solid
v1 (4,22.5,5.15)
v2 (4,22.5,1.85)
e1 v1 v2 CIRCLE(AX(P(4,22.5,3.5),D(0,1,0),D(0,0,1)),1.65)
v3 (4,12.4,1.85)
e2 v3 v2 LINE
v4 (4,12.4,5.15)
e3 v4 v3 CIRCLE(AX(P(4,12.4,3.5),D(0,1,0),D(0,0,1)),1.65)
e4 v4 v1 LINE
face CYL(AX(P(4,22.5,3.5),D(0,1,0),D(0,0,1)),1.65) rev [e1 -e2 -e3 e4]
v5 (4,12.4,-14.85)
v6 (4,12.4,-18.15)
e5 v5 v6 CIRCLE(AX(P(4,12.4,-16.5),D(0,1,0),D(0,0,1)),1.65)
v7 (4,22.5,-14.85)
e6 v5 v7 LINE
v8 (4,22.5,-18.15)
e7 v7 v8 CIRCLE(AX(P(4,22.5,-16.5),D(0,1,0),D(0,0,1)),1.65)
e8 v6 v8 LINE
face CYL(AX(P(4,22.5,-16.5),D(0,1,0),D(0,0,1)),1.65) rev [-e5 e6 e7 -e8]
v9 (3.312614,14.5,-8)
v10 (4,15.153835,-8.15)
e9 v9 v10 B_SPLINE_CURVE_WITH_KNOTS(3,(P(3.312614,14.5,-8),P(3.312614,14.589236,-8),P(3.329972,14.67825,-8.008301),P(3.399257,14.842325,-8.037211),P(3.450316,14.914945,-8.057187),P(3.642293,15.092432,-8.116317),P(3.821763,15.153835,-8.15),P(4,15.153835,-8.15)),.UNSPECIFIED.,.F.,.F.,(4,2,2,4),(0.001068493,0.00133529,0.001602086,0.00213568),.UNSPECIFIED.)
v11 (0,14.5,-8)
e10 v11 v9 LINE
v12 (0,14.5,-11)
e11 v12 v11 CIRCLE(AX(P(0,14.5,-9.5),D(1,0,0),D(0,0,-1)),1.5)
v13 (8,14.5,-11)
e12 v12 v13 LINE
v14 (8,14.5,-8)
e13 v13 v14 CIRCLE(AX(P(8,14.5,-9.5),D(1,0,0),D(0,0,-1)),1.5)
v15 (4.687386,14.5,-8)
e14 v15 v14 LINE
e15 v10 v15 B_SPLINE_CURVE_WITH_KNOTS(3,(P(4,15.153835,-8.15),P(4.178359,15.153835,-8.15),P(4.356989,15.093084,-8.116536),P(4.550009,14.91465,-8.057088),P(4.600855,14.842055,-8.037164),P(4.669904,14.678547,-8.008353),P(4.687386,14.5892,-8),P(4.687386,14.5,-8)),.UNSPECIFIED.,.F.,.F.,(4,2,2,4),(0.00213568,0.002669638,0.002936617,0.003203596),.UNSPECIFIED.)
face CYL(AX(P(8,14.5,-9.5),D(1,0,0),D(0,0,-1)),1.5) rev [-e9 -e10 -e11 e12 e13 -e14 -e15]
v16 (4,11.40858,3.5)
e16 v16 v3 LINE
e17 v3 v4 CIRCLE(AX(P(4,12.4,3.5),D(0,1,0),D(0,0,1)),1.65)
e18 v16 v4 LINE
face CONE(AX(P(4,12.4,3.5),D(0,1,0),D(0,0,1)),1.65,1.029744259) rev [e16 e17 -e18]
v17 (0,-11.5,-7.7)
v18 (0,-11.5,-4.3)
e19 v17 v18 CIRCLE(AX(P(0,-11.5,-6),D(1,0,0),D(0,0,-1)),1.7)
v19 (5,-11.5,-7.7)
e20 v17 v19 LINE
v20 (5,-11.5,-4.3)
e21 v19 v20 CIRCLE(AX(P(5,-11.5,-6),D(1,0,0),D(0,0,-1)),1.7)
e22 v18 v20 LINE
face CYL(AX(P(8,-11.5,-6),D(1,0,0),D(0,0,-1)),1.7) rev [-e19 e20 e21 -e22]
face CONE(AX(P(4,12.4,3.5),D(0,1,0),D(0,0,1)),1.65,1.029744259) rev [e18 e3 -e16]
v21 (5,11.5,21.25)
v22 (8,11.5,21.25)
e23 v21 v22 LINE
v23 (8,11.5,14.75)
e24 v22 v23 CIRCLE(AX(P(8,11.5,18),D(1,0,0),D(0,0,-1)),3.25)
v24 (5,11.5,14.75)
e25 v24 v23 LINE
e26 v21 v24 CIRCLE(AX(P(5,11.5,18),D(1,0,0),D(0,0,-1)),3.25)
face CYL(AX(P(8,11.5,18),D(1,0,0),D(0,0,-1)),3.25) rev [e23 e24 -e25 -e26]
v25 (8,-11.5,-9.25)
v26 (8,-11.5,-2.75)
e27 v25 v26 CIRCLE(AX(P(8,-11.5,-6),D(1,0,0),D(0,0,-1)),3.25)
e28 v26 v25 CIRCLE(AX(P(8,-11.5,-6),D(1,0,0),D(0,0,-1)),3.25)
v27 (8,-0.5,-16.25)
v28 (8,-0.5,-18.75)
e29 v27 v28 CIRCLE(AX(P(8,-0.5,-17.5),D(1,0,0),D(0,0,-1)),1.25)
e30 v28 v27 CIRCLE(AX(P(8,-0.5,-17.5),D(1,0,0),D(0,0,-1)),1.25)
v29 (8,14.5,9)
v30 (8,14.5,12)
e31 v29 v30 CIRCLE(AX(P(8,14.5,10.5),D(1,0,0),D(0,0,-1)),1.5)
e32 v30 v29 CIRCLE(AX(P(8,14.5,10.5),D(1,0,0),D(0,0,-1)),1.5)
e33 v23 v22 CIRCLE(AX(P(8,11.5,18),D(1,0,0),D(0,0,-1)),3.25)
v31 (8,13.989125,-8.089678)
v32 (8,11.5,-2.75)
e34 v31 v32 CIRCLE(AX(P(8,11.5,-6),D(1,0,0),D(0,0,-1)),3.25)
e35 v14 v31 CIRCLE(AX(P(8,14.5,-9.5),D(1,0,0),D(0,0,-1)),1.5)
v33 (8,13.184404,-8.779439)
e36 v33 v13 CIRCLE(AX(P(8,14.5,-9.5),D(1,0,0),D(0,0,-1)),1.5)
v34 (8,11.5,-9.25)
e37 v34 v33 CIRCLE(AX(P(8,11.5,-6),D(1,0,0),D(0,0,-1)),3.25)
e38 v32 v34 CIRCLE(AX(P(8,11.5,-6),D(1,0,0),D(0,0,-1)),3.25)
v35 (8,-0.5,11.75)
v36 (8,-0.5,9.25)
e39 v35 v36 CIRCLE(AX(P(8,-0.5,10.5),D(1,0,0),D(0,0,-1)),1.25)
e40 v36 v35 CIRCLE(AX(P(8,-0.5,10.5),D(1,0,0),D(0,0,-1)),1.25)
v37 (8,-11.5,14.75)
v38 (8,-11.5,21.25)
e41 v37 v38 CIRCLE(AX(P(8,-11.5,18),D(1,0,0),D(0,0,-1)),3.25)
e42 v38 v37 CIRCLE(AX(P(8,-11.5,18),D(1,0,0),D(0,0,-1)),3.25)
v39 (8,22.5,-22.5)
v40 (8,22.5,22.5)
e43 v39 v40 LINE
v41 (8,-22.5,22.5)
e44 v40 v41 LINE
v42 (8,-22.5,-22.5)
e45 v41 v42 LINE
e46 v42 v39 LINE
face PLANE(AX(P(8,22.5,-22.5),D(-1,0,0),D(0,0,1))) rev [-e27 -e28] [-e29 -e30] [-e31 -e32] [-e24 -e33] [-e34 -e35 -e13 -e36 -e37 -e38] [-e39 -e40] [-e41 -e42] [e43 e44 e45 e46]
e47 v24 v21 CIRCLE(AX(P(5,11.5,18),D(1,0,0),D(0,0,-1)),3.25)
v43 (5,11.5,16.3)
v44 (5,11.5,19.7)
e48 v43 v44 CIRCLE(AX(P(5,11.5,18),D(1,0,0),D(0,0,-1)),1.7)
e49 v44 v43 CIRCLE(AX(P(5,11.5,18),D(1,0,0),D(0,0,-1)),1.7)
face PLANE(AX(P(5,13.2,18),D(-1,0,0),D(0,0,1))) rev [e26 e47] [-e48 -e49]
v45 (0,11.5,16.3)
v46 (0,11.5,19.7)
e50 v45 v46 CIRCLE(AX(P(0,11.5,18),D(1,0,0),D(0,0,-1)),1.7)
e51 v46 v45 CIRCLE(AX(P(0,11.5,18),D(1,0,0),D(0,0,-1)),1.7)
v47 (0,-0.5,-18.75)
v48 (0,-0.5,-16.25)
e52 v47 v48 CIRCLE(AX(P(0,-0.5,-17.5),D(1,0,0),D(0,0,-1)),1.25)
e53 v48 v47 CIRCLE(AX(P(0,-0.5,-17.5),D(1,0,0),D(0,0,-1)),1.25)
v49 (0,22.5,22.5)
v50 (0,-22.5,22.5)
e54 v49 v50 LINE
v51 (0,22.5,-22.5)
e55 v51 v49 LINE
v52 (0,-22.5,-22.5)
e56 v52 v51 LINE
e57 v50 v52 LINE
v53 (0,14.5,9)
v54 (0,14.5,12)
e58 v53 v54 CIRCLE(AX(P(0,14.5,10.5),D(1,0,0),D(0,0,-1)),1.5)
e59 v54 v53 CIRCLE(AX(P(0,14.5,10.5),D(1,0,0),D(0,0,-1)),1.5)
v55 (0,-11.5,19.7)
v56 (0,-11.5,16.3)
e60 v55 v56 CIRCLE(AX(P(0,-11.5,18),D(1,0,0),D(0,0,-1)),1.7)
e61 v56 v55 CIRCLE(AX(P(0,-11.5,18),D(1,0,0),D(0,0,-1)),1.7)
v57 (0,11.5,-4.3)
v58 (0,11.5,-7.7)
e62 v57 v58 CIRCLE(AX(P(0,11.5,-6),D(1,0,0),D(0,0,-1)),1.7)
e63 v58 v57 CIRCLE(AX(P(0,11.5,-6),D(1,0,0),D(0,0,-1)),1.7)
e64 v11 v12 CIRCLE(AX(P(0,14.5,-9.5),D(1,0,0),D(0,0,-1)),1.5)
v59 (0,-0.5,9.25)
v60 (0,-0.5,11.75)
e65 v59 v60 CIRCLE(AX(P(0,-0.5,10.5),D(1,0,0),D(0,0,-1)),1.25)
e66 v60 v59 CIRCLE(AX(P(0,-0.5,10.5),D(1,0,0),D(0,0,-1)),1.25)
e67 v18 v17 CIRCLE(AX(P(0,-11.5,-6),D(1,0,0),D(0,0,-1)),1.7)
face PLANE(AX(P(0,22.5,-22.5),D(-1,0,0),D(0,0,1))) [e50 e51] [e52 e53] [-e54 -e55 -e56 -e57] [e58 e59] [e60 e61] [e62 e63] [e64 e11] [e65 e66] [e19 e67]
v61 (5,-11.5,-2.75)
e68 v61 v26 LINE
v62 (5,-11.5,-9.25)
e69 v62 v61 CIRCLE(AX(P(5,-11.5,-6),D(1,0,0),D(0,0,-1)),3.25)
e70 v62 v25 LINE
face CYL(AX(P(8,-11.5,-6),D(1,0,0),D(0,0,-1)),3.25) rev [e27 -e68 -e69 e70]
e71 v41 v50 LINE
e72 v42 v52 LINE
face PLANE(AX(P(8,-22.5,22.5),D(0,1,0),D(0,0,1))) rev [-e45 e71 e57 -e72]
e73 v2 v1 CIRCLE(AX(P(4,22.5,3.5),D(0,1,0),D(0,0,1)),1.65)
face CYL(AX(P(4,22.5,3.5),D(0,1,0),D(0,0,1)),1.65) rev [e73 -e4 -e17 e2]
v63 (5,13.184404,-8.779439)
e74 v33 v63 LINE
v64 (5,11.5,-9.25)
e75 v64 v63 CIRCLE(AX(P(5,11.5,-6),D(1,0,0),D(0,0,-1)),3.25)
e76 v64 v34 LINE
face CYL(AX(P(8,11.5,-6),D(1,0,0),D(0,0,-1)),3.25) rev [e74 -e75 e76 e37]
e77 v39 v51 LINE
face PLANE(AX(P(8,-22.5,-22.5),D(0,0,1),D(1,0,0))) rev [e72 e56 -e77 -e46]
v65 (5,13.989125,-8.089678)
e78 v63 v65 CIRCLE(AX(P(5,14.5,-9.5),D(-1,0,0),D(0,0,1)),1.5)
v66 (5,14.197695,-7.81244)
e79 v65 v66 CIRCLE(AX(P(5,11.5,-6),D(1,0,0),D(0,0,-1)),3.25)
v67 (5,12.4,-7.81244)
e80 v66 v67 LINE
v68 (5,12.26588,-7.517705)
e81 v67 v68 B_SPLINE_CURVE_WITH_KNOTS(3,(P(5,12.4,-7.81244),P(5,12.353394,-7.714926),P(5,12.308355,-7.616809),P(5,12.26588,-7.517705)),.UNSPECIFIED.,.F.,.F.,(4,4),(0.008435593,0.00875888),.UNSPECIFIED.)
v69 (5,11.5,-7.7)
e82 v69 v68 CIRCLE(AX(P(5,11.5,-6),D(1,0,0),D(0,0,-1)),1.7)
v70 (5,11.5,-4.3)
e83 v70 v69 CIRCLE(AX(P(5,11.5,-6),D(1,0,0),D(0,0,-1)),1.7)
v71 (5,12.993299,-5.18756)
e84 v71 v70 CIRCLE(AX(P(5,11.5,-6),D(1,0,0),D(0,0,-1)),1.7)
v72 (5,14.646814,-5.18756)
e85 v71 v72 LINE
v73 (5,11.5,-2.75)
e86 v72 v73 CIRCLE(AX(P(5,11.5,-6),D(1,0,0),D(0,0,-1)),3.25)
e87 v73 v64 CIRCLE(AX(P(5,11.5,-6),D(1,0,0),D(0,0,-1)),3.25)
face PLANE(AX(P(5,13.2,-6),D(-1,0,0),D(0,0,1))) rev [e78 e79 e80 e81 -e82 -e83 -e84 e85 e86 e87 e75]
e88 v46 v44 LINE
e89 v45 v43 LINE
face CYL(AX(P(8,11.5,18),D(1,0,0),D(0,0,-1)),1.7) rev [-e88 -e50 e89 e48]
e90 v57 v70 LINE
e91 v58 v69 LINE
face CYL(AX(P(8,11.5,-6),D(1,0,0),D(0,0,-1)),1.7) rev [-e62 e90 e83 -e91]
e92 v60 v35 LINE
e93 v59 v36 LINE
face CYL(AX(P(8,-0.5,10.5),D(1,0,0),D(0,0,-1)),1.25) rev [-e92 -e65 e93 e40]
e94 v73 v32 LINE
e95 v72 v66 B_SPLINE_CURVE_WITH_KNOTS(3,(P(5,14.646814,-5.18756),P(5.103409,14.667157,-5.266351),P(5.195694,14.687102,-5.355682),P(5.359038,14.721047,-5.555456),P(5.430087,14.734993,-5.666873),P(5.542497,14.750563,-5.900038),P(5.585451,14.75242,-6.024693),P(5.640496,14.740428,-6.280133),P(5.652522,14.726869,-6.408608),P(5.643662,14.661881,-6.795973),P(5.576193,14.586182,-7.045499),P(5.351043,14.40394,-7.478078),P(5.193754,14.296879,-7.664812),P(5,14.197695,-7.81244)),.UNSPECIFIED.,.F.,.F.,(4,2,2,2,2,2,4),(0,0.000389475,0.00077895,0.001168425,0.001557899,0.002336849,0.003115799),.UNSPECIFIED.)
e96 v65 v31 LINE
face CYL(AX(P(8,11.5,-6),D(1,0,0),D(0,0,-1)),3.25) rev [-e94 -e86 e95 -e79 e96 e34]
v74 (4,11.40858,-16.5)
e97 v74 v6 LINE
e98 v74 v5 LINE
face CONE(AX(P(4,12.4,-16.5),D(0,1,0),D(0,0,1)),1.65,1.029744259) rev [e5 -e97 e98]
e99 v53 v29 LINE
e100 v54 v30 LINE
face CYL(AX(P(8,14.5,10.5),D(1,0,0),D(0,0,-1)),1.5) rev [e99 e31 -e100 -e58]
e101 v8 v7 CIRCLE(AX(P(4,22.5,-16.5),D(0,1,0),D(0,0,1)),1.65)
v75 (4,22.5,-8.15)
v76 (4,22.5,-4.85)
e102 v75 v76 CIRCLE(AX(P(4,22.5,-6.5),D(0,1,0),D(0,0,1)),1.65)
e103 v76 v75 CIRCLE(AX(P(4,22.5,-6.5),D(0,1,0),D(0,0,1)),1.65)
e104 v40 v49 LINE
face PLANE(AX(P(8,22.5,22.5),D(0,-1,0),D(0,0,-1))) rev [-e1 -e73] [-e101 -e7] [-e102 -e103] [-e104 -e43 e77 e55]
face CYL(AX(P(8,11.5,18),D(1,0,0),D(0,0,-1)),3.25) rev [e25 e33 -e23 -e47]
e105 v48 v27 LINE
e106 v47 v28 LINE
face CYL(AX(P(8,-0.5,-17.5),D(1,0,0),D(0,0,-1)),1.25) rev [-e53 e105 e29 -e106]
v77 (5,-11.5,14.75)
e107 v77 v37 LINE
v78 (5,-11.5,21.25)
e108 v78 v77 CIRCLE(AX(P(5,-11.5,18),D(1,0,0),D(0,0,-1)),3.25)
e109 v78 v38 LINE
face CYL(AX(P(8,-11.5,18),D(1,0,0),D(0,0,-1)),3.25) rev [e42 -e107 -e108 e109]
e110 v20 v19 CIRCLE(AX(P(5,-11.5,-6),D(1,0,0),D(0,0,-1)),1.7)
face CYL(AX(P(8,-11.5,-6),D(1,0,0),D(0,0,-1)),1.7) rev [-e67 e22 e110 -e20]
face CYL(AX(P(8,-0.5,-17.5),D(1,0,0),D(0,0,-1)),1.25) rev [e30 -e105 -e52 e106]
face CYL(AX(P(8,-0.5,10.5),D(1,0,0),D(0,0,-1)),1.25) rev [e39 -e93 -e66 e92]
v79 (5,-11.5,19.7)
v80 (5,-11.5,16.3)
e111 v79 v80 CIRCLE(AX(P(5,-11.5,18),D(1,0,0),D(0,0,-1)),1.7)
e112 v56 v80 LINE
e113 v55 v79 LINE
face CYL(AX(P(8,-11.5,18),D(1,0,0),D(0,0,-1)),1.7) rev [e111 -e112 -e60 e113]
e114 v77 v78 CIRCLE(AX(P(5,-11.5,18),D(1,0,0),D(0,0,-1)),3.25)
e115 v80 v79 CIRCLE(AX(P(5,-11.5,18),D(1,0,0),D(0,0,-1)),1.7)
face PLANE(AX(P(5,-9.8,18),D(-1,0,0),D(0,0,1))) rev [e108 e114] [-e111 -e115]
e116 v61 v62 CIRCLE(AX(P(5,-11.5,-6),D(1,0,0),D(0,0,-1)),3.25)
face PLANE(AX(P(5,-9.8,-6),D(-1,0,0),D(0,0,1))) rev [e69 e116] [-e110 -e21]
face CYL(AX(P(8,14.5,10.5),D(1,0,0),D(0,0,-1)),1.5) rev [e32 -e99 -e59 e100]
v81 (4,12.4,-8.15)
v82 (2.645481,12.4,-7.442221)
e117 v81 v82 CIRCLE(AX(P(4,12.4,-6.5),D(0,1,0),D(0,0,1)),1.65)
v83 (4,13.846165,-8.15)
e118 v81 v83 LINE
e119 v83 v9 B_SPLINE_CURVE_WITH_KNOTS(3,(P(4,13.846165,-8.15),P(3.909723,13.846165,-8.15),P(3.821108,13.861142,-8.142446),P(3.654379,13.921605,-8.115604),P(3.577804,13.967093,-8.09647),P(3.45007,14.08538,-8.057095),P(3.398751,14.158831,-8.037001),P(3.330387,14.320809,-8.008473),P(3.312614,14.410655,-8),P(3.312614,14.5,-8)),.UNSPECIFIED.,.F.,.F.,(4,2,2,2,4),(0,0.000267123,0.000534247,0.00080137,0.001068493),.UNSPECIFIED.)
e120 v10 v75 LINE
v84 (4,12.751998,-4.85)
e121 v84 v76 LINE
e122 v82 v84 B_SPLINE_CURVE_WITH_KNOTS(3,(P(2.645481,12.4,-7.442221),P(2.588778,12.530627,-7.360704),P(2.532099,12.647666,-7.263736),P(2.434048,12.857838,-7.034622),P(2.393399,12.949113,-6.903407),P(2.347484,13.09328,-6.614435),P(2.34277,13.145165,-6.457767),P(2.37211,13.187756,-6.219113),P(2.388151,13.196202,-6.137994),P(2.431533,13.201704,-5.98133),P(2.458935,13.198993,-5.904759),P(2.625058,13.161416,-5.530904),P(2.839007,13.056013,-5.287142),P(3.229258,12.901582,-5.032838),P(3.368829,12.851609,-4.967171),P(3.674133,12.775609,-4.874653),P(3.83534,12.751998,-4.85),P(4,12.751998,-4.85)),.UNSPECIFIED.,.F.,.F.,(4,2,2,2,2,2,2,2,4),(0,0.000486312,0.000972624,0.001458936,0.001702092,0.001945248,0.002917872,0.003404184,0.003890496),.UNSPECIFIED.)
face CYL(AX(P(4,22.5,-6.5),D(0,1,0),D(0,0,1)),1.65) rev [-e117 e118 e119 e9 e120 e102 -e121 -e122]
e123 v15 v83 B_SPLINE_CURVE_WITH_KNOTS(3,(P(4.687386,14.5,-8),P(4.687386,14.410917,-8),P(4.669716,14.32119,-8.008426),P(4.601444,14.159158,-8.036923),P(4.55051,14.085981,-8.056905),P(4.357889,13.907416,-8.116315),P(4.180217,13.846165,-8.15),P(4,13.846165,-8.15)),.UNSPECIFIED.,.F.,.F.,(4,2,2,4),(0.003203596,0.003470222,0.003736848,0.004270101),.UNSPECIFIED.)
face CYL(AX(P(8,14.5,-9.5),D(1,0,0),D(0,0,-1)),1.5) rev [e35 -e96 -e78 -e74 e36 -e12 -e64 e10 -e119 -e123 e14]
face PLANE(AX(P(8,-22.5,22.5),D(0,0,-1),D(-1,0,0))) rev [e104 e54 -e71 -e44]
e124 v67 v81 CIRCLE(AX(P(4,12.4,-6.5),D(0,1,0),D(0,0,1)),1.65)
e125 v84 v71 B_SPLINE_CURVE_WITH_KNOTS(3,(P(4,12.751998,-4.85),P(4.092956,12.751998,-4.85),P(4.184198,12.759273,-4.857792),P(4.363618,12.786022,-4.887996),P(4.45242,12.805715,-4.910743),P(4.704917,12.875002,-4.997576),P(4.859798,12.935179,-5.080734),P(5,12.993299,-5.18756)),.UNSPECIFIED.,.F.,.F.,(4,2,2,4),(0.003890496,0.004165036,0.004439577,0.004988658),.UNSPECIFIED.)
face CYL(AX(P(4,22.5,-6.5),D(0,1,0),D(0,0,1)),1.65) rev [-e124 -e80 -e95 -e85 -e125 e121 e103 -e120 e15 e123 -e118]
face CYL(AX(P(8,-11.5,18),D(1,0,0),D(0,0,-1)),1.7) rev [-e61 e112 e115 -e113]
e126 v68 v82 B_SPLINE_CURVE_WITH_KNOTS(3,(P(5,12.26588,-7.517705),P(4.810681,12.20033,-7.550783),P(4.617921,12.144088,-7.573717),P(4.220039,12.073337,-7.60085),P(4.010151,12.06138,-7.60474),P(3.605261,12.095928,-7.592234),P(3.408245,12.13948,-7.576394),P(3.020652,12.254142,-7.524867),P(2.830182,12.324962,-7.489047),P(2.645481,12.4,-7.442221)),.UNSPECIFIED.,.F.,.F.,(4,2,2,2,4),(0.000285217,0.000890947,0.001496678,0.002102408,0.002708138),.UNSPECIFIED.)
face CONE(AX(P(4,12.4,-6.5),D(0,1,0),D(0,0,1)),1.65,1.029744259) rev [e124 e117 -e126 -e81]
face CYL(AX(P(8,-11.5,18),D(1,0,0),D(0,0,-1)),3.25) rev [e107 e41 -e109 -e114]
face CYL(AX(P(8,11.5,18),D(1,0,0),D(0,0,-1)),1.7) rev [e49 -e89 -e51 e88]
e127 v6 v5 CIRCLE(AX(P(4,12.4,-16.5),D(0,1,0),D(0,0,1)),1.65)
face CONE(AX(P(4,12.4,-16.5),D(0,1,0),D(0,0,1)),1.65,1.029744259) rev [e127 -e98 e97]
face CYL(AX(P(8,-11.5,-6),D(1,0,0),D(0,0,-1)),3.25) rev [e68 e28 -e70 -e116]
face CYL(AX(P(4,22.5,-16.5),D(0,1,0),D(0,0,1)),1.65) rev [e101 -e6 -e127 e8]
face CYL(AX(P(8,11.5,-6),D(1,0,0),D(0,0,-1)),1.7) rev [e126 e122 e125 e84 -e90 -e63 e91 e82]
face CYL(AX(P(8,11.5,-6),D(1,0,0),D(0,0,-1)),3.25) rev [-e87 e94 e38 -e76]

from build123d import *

# Parameters (mm, degrees)
SKETCH_1_W                                        = 45
SKETCH_1_H                                        = 45
BOSS_EXTRUDE_1_DEPTH                              = 8
M3_HEX_SOCKET_CAP_SCREW_COUNTERBORE_1_D           = 3.4
M3_HEX_SOCKET_CAP_SCREW_COUNTERBORE_1_CBORE_D     = 6.5
M3_HEX_SOCKET_CAP_SCREW_COUNTERBORE_1_CBORE_DEPTH = 3
LINEAR_PATTERN_1_COUNT                            = 2
LINEAR_PATTERN_1_PITCH                            = 23
LINEAR_PATTERN_2_COUNT                            = 2
LINEAR_PATTERN_2_PITCH                            = 24
LINEAR_PATTERN_2_COPY_1_D                         = 3.4
LINEAR_PATTERN_2_COPY_1_CBORE_D                   = 6.5
LINEAR_PATTERN_2_COPY_1_CBORE_DEPTH               = 3
LINEAR_PATTERN_5_COUNT                            = 3
LINEAR_PATTERN_5_PITCH                            = 10
M3_TAPPED_HOLE_1_D                                = 2.5
LINEAR_PATTERN_6_COUNT                            = 2
LINEAR_PATTERN_6_PITCH                            = 28
F_3_0_3_HOLE_1_D                                  = 3
LINEAR_PATTERN_8_COUNT                            = 2
LINEAR_PATTERN_8_PITCH                            = 20


with BuildPart() as part:
    # Sketch 1 → Boss-Extrude 1 (new body)
    with BuildSketch(Plane(origin=(0, 0, 0), x_dir=(0, 0, -1), z_dir=(1, 0, 0))):
        Rectangle(SKETCH_1_W, SKETCH_1_H)
    extrude(amount=BOSS_EXTRUDE_1_DEPTH)

    # M3 Hex Socket Cap Screw Counterbore 1 (through all)
    with Locations(Plane(origin=(8, 0, 0), x_dir=(0, 0, -1), z_dir=(1, 0, 0))):
        with Locations((-18, 11.5)):
            m3_hex_socket_cap_screw_counterbore_1 = CounterBoreHole(M3_HEX_SOCKET_CAP_SCREW_COUNTERBORE_1_D / 2, M3_HEX_SOCKET_CAP_SCREW_COUNTERBORE_1_CBORE_D / 2, M3_HEX_SOCKET_CAP_SCREW_COUNTERBORE_1_CBORE_DEPTH)

    # Linear Pattern 1: M3 Hex Socket Cap Screw Counterbore 1 ×2
    with Locations(*[(0, -i * LINEAR_PATTERN_1_PITCH, 0) for i in range(1, LINEAR_PATTERN_1_COUNT)]):
        add(m3_hex_socket_cap_screw_counterbore_1, mode=Mode.SUBTRACT)

    # Linear Pattern 2: M3 Hex Socket Cap Screw Counterbore 1 ×2
    with Locations(*[(0, 0, -i * LINEAR_PATTERN_2_PITCH) for i in range(1, LINEAR_PATTERN_2_COUNT)]):
        add(m3_hex_socket_cap_screw_counterbore_1, mode=Mode.SUBTRACT)

    # Linear Pattern 2 copy 1 (through all)
    with Locations(Plane(origin=(8, -23, -24), x_dir=(0, 0, -1), z_dir=(1, 0, 0))):
        with Locations((-18, 11.5)):
            CounterBoreHole(LINEAR_PATTERN_2_COPY_1_D / 2, LINEAR_PATTERN_2_COPY_1_CBORE_D / 2, LINEAR_PATTERN_2_COPY_1_CBORE_DEPTH)

    # Sketch 6 → M4 Tapped Hole 1 (revolve, cut)
    with BuildSketch(Plane(origin=(4, 22.5, -16.5), x_dir=(0, 0, 1), z_dir=(1, 0, 0))):
        Polygon((0, 0), (0, 11.091420021), (1.65, 10.1), (1.65, 0), align=None)
    m4_tapped_hole_1 = revolve(axis=Axis((4, 28.85, -16.5), (0, -1, 0)), mode=Mode.SUBTRACT)

    # Linear Pattern 5: M4 Tapped Hole 1 ×3
    with Locations(*[(0, 0, i * LINEAR_PATTERN_5_PITCH) for i in range(1, LINEAR_PATTERN_5_COUNT)]):
        add(m4_tapped_hole_1, mode=Mode.SUBTRACT)

    # M3 Tapped Hole 1 (through all)
    with Locations(Plane(origin=(8, 0, 0), x_dir=(0, 0, -1), z_dir=(1, 0, 0))):
        with Locations((17.5, -0.5)):
            m3_tapped_hole_1 = Hole(M3_TAPPED_HOLE_1_D / 2)

    # Linear Pattern 6: M3 Tapped Hole 1 ×2
    with Locations(*[(0, 0, i * LINEAR_PATTERN_6_PITCH) for i in range(1, LINEAR_PATTERN_6_COUNT)]):
        add(m3_tapped_hole_1, mode=Mode.SUBTRACT)

    # Ø3.0 (3) Hole 1 (through all)
    with Locations(Plane(origin=(8, 0, 0), x_dir=(0, 0, -1), z_dir=(1, 0, 0))):
        with Locations((-10.5, 14.5)):
            f_3_0_3_hole_1 = Hole(F_3_0_3_HOLE_1_D / 2)

    # Linear Pattern 8: Ø3.0 (3) Hole 1 ×2
    with Locations(*[(0, 0, -i * LINEAR_PATTERN_8_PITCH) for i in range(1, LINEAR_PATTERN_8_COUNT)]):
        add(f_3_0_3_hole_1, mode=Mode.SUBTRACT)


solid = part.part
